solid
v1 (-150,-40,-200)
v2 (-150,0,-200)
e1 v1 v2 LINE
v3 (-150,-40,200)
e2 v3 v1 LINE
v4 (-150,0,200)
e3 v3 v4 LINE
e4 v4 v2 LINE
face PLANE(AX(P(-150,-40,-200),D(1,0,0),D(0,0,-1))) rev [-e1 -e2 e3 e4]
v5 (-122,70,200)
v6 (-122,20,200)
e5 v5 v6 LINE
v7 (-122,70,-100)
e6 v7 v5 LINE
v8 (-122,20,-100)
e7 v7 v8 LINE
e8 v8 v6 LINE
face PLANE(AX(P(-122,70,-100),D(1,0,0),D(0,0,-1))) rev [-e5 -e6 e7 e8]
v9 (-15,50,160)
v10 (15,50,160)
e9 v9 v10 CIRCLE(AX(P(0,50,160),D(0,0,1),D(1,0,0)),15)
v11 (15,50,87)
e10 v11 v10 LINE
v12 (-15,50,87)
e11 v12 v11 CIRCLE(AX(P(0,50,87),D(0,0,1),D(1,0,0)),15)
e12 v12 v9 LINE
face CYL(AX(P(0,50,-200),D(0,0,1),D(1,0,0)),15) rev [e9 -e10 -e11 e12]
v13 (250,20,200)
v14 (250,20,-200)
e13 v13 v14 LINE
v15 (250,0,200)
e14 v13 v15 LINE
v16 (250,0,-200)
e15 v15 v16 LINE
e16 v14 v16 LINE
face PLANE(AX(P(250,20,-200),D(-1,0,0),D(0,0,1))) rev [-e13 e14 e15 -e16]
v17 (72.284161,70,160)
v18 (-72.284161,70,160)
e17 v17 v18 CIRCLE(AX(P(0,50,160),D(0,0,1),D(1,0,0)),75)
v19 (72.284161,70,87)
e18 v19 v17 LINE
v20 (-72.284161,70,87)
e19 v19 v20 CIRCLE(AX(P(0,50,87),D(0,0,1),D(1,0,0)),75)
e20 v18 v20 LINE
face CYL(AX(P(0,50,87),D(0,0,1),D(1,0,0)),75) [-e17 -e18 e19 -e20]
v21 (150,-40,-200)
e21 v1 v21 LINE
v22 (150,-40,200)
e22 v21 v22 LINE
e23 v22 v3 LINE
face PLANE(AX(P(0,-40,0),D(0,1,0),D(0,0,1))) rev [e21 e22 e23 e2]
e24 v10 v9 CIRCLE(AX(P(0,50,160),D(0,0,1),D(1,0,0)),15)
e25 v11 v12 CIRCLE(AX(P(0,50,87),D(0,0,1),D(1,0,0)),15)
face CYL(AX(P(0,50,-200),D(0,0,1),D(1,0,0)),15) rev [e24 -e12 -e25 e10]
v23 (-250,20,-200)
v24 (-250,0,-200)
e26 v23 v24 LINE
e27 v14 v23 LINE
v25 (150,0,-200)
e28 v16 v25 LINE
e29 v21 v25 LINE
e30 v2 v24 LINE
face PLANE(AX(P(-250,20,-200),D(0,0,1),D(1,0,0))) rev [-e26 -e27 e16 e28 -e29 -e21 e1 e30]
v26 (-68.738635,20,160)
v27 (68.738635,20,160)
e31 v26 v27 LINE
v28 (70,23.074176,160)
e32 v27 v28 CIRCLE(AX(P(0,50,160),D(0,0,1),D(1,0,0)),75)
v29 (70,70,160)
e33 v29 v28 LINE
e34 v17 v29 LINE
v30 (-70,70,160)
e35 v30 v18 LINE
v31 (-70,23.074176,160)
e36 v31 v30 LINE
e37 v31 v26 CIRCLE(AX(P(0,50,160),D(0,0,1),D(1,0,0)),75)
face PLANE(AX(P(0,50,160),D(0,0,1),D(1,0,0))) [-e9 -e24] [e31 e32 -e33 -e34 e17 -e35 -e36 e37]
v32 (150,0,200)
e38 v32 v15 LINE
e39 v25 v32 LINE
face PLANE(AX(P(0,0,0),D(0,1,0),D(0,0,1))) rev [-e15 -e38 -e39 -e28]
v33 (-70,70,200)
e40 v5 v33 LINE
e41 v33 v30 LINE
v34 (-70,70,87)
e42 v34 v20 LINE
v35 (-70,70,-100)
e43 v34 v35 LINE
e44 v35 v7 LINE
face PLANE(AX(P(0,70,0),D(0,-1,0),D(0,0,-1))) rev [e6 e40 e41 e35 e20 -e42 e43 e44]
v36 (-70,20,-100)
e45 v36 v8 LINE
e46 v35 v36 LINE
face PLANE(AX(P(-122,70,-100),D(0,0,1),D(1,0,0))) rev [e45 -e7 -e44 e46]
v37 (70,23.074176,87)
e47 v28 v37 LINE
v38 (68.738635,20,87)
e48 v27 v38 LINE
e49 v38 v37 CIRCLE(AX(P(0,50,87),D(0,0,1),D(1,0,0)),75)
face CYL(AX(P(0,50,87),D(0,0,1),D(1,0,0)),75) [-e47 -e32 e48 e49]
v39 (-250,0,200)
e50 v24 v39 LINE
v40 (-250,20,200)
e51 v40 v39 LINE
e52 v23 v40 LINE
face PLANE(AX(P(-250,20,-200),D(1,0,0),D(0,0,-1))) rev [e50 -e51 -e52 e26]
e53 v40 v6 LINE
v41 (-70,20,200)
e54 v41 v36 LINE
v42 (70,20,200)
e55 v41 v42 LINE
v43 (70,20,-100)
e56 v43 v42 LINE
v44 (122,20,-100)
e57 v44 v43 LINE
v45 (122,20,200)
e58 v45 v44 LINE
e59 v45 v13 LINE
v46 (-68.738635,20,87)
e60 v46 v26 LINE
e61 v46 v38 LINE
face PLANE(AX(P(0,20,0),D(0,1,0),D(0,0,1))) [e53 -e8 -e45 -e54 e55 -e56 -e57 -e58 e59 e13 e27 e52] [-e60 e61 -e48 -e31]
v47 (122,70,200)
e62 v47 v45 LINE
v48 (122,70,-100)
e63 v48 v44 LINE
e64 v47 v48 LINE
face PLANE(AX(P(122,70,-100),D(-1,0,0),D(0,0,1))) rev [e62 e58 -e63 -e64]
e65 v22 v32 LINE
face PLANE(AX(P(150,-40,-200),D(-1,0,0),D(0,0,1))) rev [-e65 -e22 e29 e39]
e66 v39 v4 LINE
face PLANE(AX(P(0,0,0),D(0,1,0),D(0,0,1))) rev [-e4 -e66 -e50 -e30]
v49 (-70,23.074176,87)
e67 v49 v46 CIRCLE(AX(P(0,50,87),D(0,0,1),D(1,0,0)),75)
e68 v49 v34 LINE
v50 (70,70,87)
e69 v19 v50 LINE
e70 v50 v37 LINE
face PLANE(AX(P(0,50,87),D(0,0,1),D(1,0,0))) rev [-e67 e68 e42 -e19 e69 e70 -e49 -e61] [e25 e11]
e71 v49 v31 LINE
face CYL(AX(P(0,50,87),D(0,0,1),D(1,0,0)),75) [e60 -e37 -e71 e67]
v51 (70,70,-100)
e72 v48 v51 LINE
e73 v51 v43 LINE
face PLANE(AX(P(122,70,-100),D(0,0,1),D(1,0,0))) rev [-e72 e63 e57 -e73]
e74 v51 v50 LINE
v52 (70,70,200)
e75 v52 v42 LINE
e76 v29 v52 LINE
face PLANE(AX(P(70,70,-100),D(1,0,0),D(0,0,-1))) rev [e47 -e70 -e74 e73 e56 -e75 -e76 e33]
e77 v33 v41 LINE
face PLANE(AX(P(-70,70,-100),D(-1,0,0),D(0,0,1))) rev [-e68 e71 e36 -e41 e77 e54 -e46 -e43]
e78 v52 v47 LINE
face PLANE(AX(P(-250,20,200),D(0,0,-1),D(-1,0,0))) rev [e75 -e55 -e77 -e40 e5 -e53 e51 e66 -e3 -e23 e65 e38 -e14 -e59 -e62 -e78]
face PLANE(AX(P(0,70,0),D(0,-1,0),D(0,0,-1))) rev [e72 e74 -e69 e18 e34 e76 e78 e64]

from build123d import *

# Parameters (mm, degrees)
SKETCH1_W           = 500
SKETCH1_H           = 400
BOSS_EXTRUDE1_DEPTH = 20
SKETCH2_W           = 52
SKETCH2_H           = 300
BOSS_EXTRUDE2_DEPTH = 50
SKETCH3_W           = 300
SKETCH3_H           = 400
BOSS_EXTRUDE3_DEPTH = 40
SKETCH6_R           = 75
BOSS_EXTRUDE5_DEPTH = 73
SKETCH7_R           = 15
CUT_EXTRUDE2_DEPTH  = 456.768581629


with BuildPart() as part:
    # Sketch1 → Boss-Extrude1 (new body)
    with BuildSketch(Plane(origin=(0, 0, 0), x_dir=(1, 0, 0), z_dir=(0, 1, 0))):
        Rectangle(SKETCH1_W, SKETCH1_H)
    extrude(amount=BOSS_EXTRUDE1_DEPTH)

    # Sketch2 → Boss-Extrude2 (add)
    with BuildSketch(Plane(origin=(0, 20, 0), x_dir=(1, 0, 0), z_dir=(0, 1, 0))):
        with Locations((-96, -50)):
            Rectangle(SKETCH2_W, SKETCH2_H)
        with Locations((96, -50)):
            Rectangle(SKETCH2_W, SKETCH2_H)
    extrude(amount=BOSS_EXTRUDE2_DEPTH)

    # Sketch3 → Boss-Extrude3 (add)
    with BuildSketch(Plane.XZ):
        Rectangle(SKETCH3_W, SKETCH3_H)
    extrude(amount=BOSS_EXTRUDE3_DEPTH)

    # Sketch6 → Boss-Extrude5 (add)
    with BuildSketch(Plane.XY.offset(160)):
        with Locations((0, 50)):
            Circle(SKETCH6_R)
    extrude(amount=-BOSS_EXTRUDE5_DEPTH)

    # Sketch7 → Cut-Extrude2 (cut, through all)
    with BuildSketch(Plane.XY.offset(160)):
        with Locations((0, 50)):
            Circle(SKETCH7_R)
    extrude(amount=-CUT_EXTRUDE2_DEPTH, mode=Mode.SUBTRACT)


solid = part.part
